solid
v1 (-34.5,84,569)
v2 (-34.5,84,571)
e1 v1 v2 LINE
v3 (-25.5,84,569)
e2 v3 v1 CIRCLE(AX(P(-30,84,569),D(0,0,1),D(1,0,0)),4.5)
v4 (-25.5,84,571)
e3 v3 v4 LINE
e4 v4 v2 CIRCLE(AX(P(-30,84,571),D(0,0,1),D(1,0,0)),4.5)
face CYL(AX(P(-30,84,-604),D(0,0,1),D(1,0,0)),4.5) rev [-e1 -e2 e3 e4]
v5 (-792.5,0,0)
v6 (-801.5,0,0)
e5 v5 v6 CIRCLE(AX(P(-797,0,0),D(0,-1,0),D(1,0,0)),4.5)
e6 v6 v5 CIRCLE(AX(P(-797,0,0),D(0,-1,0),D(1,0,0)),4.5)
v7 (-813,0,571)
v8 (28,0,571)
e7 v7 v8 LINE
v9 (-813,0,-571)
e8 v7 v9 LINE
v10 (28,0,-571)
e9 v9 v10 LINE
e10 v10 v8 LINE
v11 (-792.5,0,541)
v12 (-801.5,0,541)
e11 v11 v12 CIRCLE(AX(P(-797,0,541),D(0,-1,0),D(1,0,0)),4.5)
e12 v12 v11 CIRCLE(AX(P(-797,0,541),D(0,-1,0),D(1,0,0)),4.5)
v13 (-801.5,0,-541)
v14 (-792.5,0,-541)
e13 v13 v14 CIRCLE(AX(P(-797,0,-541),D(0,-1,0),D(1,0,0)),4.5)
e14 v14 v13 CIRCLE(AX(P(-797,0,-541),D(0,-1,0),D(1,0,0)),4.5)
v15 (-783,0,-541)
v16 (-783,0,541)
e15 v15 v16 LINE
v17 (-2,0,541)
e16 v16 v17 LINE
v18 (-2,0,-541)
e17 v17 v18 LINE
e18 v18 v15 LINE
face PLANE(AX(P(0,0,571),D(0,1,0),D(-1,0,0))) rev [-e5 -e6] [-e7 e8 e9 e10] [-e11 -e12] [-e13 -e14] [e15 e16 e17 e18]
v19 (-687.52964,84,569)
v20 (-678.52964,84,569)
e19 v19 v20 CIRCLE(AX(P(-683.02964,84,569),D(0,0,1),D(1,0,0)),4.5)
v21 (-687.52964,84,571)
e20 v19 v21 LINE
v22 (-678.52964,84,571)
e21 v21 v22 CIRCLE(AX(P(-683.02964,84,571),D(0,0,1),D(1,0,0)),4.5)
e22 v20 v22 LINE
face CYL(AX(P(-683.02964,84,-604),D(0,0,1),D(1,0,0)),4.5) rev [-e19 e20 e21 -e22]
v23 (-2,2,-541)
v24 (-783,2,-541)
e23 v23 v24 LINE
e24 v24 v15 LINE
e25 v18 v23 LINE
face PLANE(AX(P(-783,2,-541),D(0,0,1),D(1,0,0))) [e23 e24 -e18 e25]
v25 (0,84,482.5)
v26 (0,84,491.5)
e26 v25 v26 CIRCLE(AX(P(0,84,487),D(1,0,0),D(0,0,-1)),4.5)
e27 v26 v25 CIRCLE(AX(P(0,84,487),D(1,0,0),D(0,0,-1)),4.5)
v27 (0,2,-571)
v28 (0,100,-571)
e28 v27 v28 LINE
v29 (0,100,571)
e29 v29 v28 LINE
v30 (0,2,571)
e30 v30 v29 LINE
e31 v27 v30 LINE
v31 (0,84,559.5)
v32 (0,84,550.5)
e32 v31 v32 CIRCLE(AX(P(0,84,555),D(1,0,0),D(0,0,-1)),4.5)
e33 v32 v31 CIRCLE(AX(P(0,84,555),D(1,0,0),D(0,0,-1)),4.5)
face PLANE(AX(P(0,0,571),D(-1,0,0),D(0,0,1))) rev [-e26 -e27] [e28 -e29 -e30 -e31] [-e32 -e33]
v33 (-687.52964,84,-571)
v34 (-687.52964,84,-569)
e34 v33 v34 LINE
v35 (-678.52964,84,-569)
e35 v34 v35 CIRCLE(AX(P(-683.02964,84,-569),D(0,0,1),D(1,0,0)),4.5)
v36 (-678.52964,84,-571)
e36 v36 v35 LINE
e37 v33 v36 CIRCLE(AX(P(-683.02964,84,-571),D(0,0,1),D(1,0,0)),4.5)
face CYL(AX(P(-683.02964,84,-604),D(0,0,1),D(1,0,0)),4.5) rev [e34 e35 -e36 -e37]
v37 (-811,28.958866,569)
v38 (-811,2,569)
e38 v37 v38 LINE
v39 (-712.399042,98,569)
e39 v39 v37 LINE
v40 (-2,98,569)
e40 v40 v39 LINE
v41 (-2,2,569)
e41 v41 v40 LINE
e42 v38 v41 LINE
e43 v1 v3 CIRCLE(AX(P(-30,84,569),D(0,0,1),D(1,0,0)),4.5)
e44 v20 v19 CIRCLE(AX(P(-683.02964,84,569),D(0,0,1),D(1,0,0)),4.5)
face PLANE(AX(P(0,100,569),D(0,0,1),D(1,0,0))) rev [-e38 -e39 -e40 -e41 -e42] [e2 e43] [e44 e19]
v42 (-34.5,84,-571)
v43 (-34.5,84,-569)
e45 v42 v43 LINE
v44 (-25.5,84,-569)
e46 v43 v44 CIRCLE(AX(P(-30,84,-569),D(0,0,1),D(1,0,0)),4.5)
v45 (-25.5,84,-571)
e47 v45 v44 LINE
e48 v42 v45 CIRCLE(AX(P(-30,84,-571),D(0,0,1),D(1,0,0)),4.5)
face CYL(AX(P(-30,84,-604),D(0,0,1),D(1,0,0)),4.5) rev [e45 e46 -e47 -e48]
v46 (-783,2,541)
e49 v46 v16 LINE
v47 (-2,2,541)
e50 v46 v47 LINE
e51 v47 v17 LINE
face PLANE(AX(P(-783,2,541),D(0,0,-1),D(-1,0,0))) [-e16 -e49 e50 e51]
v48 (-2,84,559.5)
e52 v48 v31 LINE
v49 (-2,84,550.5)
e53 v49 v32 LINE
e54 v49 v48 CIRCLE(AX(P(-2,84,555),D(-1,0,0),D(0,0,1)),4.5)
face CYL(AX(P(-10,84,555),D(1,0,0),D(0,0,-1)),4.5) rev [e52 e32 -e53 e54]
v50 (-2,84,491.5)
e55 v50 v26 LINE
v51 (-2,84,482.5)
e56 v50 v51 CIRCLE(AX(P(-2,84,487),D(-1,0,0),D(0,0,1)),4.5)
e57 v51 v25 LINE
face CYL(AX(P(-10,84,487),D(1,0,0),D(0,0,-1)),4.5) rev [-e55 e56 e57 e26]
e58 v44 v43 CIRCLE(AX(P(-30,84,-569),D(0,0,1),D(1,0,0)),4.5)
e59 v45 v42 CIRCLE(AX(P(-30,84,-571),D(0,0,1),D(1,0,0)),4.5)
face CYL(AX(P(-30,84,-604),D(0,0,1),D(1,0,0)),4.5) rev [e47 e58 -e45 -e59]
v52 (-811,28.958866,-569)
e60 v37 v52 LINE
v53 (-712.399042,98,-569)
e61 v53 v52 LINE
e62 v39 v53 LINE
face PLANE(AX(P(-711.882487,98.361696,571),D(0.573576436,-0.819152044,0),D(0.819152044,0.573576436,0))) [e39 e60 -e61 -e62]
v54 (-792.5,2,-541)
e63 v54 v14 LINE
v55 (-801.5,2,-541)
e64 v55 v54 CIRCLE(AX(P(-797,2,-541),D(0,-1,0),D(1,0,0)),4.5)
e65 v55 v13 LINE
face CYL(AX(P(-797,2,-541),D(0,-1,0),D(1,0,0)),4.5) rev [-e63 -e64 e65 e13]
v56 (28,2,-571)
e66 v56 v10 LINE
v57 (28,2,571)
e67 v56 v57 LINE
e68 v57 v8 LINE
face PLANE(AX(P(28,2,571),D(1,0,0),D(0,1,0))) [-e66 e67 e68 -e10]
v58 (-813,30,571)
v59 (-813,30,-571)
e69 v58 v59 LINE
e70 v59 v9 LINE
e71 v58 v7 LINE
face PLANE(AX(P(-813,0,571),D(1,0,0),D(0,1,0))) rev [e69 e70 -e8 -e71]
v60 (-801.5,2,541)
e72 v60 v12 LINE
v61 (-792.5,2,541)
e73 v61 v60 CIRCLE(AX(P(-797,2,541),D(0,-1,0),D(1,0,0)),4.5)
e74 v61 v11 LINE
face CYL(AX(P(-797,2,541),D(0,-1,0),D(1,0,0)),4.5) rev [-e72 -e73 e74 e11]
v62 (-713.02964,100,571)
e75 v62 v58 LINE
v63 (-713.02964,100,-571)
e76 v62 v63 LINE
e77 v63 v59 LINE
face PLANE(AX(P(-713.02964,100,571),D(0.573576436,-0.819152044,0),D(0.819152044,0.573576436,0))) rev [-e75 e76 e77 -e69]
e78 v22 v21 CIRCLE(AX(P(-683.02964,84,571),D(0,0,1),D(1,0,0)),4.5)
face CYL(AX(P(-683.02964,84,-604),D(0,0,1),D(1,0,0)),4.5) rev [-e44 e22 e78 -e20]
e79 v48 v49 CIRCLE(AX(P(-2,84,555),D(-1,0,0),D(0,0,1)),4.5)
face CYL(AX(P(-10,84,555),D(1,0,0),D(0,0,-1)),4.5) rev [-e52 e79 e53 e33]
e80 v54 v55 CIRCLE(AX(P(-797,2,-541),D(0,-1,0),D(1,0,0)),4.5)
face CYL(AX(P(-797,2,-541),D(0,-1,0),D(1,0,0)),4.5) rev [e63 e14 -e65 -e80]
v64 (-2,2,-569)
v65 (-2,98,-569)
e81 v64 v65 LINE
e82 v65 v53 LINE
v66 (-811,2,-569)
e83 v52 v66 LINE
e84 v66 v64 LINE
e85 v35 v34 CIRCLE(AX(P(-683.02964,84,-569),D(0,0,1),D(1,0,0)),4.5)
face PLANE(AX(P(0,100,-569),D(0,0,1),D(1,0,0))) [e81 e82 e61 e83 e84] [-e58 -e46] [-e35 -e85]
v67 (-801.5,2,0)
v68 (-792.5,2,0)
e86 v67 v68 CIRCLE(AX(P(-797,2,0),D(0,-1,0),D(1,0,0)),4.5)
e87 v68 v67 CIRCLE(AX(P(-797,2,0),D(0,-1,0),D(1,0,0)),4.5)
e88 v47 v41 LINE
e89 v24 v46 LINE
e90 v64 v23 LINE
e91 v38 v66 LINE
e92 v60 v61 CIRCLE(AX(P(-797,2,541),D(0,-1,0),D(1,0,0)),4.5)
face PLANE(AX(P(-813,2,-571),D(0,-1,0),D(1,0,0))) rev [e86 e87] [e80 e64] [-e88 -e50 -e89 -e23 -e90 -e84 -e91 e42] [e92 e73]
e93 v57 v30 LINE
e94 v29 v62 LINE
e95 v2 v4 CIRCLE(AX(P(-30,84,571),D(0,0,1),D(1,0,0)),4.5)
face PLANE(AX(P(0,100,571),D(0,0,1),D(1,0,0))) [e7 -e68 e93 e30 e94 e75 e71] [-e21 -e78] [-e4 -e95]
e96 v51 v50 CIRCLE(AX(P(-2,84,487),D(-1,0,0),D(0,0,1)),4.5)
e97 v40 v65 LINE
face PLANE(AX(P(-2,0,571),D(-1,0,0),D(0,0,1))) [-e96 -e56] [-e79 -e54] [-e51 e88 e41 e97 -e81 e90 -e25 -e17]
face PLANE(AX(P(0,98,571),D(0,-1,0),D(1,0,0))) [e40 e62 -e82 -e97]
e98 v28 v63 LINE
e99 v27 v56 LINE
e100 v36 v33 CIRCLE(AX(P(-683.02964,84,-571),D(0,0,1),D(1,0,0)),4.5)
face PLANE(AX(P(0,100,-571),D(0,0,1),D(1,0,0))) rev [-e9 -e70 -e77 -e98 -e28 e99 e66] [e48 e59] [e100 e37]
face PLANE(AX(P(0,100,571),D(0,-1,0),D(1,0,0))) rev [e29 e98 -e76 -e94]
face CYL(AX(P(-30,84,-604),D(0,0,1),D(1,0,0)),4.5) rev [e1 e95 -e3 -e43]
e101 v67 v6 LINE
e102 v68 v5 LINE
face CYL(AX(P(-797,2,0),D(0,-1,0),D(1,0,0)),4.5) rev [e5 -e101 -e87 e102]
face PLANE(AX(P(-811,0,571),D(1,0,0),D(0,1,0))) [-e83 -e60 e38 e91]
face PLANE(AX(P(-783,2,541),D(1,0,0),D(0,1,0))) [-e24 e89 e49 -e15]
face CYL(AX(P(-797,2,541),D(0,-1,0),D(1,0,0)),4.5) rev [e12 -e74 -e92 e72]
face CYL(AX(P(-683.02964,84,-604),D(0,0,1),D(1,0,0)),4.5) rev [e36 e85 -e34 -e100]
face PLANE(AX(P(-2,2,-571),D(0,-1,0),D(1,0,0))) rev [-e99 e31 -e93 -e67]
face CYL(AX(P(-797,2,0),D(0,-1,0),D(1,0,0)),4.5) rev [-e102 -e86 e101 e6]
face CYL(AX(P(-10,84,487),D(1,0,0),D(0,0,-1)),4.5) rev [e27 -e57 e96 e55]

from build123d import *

# Parameters (mm, degrees)
EXTRUDE_1_DEPTH     = 571
SHELL_1_T           = -2
SKETCH_2_W          = 30
SKETCH_2_H          = 1142
EXTRUDE_2_DEPTH     = 2
SKETCH_3_R          = 4.5
CUT_EXTRUDE_1_DEPTH = 1175
EXTRUDE_3_DEPTH     = 2
SKETCH_6_R          = 4.5
CUT_EXTRUDE_2_DEPTH = 2
SKETCH_7_R          = 4.5
CUT_EXTRUDE_3_DEPTH = 10


with BuildPart() as part:
    # 草图1 → 凸台-拉伸1 (new, symmetric)
    with BuildSketch(Plane.XY):
        Polygon((0, 0), (-813, 0), (-813, 30), (-713.029639528, 100), (0, 100), align=None)
    extrude(amount=EXTRUDE_1_DEPTH, both=True)

    # 抽壳1
    shell_1_openings = [part.faces().sort_by_distance(p)[0] for p in [
        (-406.5, 0, 0),
    ]]
    offset(amount=SHELL_1_T, openings=shell_1_openings, kind=Kind.INTERSECTION)

    # 草图2 → 凸台-拉伸2 (add)
    with BuildSketch(Plane.XZ):
        with Locations((13, 0)):
            Rectangle(SKETCH_2_W, SKETCH_2_H)
    extrude(amount=-EXTRUDE_2_DEPTH)

    # 草图3 → 切除-拉伸1 (cut)
    with BuildSketch(Plane.XY.offset(571)):
        with Locations((-683.029639528, 84)):
            Circle(SKETCH_3_R)
        with Locations((-30, 84)):
            Circle(SKETCH_3_R)
    extrude(amount=-CUT_EXTRUDE_1_DEPTH, mode=Mode.SUBTRACT)

    # 草图5 → 凸台-拉伸3 (add)
    with BuildSketch(Plane.XZ):
        Polygon((-783, 541), (0, 541), (0, 571), (-813, 571), (-813, -571), (0, -571), (0, -541), (-783, -541), align=None)
    extrude(amount=-EXTRUDE_3_DEPTH)

    # 草图6 → 切除-拉伸2 (cut)
    with BuildSketch(Plane.XZ):
        with Locations((-797, 541)):
            Circle(SKETCH_6_R)
        with Locations((-797, -541)):
            Circle(SKETCH_6_R)
        with Locations((-797, 0)):
            Circle(SKETCH_6_R)
    extrude(amount=-CUT_EXTRUDE_2_DEPTH, mode=Mode.SUBTRACT)

    # 草图7 → 切除-拉伸3 (cut)
    with BuildSketch(Plane(origin=(0, 0, 0), x_dir=(0, 0, -1), z_dir=(1, 0, 0))):
        with Locations((-555, 84)):
            Circle(SKETCH_7_R)
        with Locations((-487, 84)):
            Circle(SKETCH_7_R)
    extrude(amount=-CUT_EXTRUDE_3_DEPTH, mode=Mode.SUBTRACT)


solid = part.part
